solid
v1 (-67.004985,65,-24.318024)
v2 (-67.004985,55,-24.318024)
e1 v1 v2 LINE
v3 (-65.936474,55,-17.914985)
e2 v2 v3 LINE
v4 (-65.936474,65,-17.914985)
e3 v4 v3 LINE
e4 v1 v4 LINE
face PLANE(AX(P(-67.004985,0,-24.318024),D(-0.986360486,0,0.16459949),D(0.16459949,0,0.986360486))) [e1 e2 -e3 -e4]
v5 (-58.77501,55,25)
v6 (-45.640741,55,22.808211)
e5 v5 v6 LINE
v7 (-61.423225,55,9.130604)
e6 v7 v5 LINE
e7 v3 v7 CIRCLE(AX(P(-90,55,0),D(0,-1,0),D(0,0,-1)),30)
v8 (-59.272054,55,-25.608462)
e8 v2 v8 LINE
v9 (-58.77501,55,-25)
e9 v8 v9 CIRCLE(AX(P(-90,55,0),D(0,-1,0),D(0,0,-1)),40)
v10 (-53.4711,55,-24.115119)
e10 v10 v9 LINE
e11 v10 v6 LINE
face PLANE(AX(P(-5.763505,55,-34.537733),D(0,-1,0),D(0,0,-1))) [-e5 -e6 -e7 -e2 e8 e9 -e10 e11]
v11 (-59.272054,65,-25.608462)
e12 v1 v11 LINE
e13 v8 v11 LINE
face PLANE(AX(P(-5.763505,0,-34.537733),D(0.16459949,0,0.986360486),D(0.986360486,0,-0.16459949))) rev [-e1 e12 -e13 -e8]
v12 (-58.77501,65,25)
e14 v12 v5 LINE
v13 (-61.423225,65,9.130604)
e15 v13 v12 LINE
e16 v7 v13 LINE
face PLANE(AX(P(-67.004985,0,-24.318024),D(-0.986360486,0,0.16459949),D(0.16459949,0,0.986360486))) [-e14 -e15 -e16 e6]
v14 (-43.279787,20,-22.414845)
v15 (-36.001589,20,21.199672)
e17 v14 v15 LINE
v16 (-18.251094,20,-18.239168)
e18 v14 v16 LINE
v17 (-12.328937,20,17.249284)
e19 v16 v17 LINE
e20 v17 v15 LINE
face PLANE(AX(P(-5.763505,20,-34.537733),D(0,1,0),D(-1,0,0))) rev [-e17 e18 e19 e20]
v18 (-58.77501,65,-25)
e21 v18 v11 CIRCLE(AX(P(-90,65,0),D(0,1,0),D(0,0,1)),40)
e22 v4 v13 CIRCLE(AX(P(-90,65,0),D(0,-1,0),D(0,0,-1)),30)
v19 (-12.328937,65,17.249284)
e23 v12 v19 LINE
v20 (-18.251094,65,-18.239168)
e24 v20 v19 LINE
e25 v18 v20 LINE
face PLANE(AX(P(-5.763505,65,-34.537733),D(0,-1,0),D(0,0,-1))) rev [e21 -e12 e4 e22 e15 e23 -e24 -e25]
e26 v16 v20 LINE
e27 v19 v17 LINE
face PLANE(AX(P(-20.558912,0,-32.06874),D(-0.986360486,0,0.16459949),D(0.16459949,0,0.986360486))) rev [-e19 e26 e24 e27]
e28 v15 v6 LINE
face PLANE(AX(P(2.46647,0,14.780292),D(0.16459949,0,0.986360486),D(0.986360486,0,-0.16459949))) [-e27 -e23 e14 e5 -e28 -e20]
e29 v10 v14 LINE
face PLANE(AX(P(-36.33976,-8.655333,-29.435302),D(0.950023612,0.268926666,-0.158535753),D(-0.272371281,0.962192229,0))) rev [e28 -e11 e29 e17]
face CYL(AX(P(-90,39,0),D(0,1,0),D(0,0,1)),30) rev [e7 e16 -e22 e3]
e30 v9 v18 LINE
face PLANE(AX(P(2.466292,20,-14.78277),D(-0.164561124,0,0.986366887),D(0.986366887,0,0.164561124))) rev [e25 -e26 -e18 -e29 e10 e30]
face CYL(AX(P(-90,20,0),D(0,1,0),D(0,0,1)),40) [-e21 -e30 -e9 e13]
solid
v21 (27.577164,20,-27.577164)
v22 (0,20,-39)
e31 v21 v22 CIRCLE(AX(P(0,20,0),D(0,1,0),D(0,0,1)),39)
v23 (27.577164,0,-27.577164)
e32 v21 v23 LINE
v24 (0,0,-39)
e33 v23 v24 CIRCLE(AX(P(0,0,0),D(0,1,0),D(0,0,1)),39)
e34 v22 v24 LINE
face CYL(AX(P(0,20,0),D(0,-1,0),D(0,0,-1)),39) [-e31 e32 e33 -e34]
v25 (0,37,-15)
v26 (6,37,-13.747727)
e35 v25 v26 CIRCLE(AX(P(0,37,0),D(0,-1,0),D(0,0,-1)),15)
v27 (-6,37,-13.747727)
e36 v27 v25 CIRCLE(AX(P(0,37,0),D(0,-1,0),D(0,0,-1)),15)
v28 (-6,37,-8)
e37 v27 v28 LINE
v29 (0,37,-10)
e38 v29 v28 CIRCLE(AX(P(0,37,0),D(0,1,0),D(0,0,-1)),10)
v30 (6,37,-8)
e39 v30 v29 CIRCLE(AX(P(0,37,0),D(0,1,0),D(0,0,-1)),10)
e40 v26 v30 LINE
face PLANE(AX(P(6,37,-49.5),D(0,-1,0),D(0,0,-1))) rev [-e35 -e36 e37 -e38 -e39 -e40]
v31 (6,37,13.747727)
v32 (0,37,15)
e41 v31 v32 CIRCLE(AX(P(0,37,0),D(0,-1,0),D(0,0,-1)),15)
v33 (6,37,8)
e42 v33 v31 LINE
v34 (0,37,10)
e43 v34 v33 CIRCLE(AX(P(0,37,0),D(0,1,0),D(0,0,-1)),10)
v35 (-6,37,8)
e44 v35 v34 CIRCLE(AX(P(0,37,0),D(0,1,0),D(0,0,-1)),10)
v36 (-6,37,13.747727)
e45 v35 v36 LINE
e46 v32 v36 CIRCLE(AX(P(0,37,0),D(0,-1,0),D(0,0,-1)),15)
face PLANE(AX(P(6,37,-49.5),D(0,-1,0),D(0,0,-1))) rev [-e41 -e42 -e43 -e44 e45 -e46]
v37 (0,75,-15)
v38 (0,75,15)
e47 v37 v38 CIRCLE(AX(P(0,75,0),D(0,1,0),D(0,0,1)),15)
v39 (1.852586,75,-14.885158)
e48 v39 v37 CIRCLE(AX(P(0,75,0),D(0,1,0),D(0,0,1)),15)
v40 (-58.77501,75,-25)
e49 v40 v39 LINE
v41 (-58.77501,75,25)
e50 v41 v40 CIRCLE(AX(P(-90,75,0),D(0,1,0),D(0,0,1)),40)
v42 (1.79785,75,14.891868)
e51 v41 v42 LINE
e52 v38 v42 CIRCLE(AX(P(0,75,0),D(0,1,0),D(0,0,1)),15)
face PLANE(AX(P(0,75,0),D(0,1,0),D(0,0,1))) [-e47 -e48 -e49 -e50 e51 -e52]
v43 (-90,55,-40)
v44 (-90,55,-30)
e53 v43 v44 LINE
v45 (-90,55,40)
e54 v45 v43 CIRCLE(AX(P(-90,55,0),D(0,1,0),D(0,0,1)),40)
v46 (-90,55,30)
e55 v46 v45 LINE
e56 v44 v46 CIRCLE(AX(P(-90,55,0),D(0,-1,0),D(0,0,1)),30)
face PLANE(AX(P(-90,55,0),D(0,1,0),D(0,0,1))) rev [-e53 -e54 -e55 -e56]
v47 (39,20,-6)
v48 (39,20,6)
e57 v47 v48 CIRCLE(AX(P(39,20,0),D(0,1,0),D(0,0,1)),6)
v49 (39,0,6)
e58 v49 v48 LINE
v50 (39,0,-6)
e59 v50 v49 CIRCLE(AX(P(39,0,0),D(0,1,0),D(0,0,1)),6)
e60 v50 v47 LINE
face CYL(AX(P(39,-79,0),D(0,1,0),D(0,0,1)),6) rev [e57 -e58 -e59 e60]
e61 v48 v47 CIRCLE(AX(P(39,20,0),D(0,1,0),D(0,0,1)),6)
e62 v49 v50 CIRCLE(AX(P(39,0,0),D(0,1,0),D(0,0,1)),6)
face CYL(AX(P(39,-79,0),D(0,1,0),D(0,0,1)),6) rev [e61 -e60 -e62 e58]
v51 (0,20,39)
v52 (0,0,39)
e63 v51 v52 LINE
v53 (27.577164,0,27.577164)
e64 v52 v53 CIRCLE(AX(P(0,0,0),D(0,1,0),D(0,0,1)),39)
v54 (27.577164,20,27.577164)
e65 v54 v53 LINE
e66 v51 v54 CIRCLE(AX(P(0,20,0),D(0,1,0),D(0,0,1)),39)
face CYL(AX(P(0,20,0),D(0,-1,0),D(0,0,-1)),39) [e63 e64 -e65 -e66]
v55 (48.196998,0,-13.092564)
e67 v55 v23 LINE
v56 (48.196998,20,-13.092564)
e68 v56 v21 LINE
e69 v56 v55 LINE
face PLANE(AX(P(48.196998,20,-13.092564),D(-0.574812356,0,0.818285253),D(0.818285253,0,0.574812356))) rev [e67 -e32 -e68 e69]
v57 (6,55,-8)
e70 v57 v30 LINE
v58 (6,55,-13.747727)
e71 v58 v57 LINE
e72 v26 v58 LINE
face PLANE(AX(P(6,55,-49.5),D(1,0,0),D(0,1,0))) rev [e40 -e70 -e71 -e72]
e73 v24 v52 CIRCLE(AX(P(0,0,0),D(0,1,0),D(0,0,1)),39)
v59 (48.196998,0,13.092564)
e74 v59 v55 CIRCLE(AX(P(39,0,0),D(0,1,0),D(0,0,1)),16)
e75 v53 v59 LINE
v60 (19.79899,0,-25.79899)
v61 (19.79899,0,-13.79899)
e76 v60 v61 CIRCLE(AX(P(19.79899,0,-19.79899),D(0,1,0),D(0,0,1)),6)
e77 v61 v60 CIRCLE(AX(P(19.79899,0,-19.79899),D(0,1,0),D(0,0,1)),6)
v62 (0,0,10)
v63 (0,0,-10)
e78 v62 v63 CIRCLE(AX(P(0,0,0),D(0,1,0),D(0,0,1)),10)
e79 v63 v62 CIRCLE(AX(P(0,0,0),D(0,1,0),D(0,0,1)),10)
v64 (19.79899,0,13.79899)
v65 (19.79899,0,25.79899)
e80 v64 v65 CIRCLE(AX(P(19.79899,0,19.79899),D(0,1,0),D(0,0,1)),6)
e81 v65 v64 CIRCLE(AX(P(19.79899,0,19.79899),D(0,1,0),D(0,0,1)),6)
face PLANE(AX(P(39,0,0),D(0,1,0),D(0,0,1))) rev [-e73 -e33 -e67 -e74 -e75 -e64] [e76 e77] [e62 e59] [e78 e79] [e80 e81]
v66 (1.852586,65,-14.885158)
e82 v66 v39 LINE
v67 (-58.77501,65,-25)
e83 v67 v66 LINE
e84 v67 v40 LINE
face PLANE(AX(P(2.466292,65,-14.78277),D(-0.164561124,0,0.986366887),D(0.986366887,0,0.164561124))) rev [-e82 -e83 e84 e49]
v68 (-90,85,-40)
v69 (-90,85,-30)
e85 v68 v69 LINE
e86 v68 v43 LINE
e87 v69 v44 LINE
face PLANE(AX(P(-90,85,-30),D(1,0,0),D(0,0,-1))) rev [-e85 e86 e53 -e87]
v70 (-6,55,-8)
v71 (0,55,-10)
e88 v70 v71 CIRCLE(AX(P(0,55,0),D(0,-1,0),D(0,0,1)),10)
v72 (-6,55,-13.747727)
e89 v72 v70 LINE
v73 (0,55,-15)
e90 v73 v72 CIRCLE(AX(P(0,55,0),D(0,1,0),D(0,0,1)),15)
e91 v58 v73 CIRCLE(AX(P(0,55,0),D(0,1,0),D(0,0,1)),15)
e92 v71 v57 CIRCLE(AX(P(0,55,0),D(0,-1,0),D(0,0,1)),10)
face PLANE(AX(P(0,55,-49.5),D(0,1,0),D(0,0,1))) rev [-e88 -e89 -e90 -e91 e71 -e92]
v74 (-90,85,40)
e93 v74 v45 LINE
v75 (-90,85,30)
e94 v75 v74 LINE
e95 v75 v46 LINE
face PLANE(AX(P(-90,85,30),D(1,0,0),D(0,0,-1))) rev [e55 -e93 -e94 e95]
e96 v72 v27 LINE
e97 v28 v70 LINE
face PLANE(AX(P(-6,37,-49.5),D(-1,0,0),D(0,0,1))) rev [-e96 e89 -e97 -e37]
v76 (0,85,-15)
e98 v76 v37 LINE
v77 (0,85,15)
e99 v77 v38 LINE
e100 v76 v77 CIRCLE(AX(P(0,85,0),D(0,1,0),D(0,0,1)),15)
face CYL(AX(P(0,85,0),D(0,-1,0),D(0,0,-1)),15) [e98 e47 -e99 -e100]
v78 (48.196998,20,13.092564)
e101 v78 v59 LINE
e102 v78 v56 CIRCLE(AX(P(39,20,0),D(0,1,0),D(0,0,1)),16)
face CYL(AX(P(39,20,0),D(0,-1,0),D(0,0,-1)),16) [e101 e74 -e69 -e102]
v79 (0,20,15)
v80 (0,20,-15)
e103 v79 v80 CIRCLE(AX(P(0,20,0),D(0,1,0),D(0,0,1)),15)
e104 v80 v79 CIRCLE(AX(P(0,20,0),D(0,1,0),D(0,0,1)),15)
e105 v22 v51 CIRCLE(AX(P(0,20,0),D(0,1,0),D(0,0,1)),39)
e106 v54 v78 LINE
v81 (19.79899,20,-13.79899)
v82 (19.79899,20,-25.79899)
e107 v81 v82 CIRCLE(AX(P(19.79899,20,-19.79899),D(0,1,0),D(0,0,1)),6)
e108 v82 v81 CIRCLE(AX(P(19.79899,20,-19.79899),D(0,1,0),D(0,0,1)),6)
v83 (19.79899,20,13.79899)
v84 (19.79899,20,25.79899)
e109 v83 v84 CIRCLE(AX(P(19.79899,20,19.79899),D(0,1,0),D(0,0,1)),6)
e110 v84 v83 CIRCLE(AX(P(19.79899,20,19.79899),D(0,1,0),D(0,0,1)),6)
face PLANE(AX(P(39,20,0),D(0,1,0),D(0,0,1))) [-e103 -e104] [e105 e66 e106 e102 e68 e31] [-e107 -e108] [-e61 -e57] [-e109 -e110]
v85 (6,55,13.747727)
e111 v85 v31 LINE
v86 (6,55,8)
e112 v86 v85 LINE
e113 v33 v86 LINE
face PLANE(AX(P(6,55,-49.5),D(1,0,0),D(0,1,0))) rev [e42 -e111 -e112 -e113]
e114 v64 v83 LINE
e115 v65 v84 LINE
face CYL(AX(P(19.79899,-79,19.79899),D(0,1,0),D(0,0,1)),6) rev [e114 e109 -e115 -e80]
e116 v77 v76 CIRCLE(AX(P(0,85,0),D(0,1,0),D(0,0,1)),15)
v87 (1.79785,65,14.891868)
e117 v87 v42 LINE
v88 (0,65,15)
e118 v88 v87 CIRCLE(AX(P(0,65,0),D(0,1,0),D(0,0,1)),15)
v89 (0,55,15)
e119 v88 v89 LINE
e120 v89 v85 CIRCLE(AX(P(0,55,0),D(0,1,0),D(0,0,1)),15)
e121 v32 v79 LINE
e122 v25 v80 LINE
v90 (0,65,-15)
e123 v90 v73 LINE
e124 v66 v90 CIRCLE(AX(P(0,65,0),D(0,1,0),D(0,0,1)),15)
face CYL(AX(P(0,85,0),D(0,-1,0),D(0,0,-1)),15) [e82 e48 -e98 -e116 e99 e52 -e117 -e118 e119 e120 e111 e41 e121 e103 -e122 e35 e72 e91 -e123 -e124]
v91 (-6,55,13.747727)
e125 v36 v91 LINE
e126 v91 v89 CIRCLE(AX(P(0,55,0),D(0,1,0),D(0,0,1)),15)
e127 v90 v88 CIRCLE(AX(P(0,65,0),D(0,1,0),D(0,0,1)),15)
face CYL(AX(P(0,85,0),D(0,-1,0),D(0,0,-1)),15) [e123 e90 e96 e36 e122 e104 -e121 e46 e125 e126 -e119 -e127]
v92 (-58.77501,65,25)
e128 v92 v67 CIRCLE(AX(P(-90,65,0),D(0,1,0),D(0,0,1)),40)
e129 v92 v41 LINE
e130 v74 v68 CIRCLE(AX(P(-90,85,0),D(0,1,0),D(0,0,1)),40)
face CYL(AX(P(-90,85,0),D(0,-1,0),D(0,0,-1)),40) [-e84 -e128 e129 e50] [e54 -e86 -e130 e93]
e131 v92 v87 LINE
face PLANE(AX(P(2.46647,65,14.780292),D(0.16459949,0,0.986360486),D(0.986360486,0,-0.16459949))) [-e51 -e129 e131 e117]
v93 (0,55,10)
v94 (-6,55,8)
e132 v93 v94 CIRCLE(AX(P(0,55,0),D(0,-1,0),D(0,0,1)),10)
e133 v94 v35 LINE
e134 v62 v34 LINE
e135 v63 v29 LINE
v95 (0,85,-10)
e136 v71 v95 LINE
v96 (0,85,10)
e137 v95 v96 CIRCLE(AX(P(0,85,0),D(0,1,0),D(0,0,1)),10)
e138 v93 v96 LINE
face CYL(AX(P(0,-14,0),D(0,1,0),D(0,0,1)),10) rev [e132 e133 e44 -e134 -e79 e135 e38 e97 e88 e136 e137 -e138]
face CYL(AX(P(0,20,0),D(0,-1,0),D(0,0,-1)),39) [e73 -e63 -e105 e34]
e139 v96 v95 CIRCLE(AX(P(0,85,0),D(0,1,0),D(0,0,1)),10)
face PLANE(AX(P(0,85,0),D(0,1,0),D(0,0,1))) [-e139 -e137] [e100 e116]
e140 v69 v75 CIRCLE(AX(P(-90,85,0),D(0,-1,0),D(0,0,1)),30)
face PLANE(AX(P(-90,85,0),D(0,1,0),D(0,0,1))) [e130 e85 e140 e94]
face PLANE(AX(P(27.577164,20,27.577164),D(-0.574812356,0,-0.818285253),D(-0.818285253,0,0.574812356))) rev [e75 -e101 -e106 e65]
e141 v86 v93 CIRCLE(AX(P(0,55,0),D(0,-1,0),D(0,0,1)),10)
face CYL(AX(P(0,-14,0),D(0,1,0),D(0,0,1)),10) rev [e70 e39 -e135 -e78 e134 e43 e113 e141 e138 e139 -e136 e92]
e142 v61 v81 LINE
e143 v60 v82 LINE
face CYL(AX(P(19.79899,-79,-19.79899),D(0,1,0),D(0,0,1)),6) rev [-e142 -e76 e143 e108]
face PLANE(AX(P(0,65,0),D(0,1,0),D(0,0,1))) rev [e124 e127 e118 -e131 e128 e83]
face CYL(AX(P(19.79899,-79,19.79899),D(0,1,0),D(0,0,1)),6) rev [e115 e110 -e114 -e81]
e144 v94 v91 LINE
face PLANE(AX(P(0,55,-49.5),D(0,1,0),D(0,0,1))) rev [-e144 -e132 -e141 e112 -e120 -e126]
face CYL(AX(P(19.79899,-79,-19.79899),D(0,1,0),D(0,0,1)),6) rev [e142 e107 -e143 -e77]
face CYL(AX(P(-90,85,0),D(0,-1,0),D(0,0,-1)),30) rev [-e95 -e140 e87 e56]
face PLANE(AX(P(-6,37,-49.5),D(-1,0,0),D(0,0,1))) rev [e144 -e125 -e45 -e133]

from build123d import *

# Parameters (mm, degrees)
BASE_FLANGE_DEPTH          = 20
COLUMN_SKETCH_R            = 15
COLUMN_30_DEPTH            = 65
CLAMP_JAW_DEPTH            = 10
CLAMP_JAW_DEPTH_BACK       = 20
JAW_START                  = -10
JAW_SUPPORT_PLATE_DEPTH    = 10
SUPPORT_WEB_DEPTH          = 50
JAW_START_2                = -45
JAW_RELIEF_CUT_DEPTH       = 45
CLAMP_START                = -46
CLAMP_BORE_SKETCH_R        = 30
CLAMP_BORE_60_DEPTH        = 46
COLUMN_BORE_SKETCH_R       = 10
COLUMN_BORE_20_DEPTH       = 99
MOUNTING_HOLES_SKETCH_R    = 6
MOUNTING_HOLES_3X_12_DEPTH = 99
COLUMN_SLOT_DEPTH          = 49.5


with BuildPart() as part:
    # Base Flange Sketch → Base Flange (new body)
    with BuildSketch(Plane(origin=(0, 0, 0), x_dir=(1, 0, 0), z_dir=(0, 1, 0))):
        with BuildLine():
            Line((48.196997695, 13.09256405), (27.577164466, 27.577164466))
            ThreePointArc((27.577164466, 27.577164466), (-39, 0), (27.577164466, -27.577164466))
            Line((27.577164466, -27.577164466), (48.196997695, -13.09256405))
            ThreePointArc((48.196997695, -13.09256405), (55, 0), (48.196997695, 13.09256405))
        make_face()
    extrude(amount=BASE_FLANGE_DEPTH)

    # Column Sketch → Column Ø30 (add)
    with BuildSketch(Plane(origin=(0, 20, 0), x_dir=(1, 0, 0), z_dir=(0, 1, 0))):
        with Locations(Location((0, 0, 0), (0, 0, 270))):
            Circle(COLUMN_SKETCH_R)
    extrude(amount=COLUMN_30_DEPTH)



with BuildPart() as body_2:
    # Clamp Jaw Sketch → Clamp Jaw (new, two sides: drawn at the far end of the back side and taken through both)
    with BuildSketch(Plane(origin=(0, 75, 0), x_dir=(1, 0, 0), z_dir=(0, 1, 0)).offset(-CLAMP_JAW_DEPTH_BACK)):
        with BuildLine():
            Line((-90, 30), (-90, 40))
            ThreePointArc((-90, 40), (-50, 0), (-90, -40))
            Line((-90, -40), (-90, -30))
            ThreePointArc((-90, -30), (-60, 0), (-90, 30))
        make_face()
    extrude(amount=CLAMP_JAW_DEPTH + CLAMP_JAW_DEPTH_BACK)


with BuildPart() as part_1:
    add(part.part)

    add(body_2.part)  # Jaw Support Plate merges body 2
    # Jaw Support Plate Sketch → Jaw Support Plate (add)
    with BuildSketch(Plane(origin=(0, 75, 0), x_dir=(1, 0, 0), z_dir=(0, 1, 0)).offset(JAW_START)):
        with BuildLine():
            ThreePointArc((1.852586009, 14.885157879), (-14.98589618, -0.650319682), (3.13508959, -14.668715461))
            Line((3.13508959, -14.668715461), (-58.775010008, -25))
            ThreePointArc((-58.775010008, -25), (-50, 0), (-58.775010008, 25))
            Line((-58.775010008, 25), (1.852586009, 14.885157879))
        make_face()
    extrude(amount=JAW_SUPPORT_PLATE_DEPTH)

    # Column Bore Sketch → Column Bore Ø20 (cut)
    with BuildSketch(Plane(origin=(0, 85, 0), x_dir=(1, 0, 0), z_dir=(0, 1, 0))):
        with Locations(Location((0, 0, 0), (0, 0, 270))):
            Circle(COLUMN_BORE_SKETCH_R)
    extrude(amount=-COLUMN_BORE_20_DEPTH, mode=Mode.SUBTRACT)

    # Mounting Holes Sketch → Mounting Holes 3xØ12 (cut)
    with BuildSketch(Plane(origin=(0, 20, 0), x_dir=(1, 0, 0), z_dir=(0, 1, 0))):
        with Locations(Location((39, 0, 0), (0, 0, 270))):
            Circle(MOUNTING_HOLES_SKETCH_R)
        with Locations(Location((19.798989873, 19.798989873, 0), (0, 0, 270))):
            Circle(MOUNTING_HOLES_SKETCH_R)
        with Locations(Location((19.798989873, -19.798989873, 0), (0, 0, 270))):
            Circle(MOUNTING_HOLES_SKETCH_R)
    extrude(amount=-MOUNTING_HOLES_3X_12_DEPTH, mode=Mode.SUBTRACT)

    # Column Slot Sketch → Column Slot (cut, symmetric)
    with BuildSketch(Plane.XY):
        Polygon((0, 55), (6, 55), (6, 37), (-6, 37), (-6, 55), align=None)
    extrude(amount=COLUMN_SLOT_DEPTH, both=True, mode=Mode.SUBTRACT)


with BuildPart() as body_2_2:
    # Support Web Sketch → Support Web (new body)
    with BuildSketch(Plane(origin=(2.466469942, 0, 14.78029176), x_dir=(0.9863604857263539, 0, -0.1645994902716021), z_dir=(0.1645994902716021, 0, 0.9863604857263539))):
        Polygon((-15, 20), (-15, 65), (-62.088334677, 65), (-62.088334677, 55), (-48.772443715, 55), (-39, 20), align=None)
    extrude(amount=-SUPPORT_WEB_DEPTH)

    # Jaw Relief Cut Sketch → Jaw Relief Cut (cut)
    with BuildSketch(Plane(origin=(0, 65, 0), x_dir=(1, 0, 0), z_dir=(0, 1, 0)).offset(JAW_START_2)):
        with BuildLine():
            ThreePointArc((-59.272053619, 25.608461711), (-59.02203787, 25.305451236), (-58.775010008, 25))
            Line((-58.775010008, 25), (-18.251093745, 18.239167606))
            Line((-18.251093745, 18.239167606), (-20.558911858, 32.068740172))
            Line((-20.558911858, 32.068740172), (-59.272053619, 25.608461711))
        make_face()
    extrude(amount=JAW_RELIEF_CUT_DEPTH, mode=Mode.SUBTRACT)

    # Clamp Bore Sketch → Clamp Bore Ø60 (cut)
    with BuildSketch(Plane(origin=(0, 85, 0), x_dir=(1, 0, 0), z_dir=(0, 1, 0)).offset(CLAMP_START)):
        with Locations((-90, 0)):
            Circle(CLAMP_BORE_SKETCH_R)
    extrude(amount=CLAMP_BORE_60_DEPTH, mode=Mode.SUBTRACT)


solid = Compound([part_1.part, body_2_2.part])
